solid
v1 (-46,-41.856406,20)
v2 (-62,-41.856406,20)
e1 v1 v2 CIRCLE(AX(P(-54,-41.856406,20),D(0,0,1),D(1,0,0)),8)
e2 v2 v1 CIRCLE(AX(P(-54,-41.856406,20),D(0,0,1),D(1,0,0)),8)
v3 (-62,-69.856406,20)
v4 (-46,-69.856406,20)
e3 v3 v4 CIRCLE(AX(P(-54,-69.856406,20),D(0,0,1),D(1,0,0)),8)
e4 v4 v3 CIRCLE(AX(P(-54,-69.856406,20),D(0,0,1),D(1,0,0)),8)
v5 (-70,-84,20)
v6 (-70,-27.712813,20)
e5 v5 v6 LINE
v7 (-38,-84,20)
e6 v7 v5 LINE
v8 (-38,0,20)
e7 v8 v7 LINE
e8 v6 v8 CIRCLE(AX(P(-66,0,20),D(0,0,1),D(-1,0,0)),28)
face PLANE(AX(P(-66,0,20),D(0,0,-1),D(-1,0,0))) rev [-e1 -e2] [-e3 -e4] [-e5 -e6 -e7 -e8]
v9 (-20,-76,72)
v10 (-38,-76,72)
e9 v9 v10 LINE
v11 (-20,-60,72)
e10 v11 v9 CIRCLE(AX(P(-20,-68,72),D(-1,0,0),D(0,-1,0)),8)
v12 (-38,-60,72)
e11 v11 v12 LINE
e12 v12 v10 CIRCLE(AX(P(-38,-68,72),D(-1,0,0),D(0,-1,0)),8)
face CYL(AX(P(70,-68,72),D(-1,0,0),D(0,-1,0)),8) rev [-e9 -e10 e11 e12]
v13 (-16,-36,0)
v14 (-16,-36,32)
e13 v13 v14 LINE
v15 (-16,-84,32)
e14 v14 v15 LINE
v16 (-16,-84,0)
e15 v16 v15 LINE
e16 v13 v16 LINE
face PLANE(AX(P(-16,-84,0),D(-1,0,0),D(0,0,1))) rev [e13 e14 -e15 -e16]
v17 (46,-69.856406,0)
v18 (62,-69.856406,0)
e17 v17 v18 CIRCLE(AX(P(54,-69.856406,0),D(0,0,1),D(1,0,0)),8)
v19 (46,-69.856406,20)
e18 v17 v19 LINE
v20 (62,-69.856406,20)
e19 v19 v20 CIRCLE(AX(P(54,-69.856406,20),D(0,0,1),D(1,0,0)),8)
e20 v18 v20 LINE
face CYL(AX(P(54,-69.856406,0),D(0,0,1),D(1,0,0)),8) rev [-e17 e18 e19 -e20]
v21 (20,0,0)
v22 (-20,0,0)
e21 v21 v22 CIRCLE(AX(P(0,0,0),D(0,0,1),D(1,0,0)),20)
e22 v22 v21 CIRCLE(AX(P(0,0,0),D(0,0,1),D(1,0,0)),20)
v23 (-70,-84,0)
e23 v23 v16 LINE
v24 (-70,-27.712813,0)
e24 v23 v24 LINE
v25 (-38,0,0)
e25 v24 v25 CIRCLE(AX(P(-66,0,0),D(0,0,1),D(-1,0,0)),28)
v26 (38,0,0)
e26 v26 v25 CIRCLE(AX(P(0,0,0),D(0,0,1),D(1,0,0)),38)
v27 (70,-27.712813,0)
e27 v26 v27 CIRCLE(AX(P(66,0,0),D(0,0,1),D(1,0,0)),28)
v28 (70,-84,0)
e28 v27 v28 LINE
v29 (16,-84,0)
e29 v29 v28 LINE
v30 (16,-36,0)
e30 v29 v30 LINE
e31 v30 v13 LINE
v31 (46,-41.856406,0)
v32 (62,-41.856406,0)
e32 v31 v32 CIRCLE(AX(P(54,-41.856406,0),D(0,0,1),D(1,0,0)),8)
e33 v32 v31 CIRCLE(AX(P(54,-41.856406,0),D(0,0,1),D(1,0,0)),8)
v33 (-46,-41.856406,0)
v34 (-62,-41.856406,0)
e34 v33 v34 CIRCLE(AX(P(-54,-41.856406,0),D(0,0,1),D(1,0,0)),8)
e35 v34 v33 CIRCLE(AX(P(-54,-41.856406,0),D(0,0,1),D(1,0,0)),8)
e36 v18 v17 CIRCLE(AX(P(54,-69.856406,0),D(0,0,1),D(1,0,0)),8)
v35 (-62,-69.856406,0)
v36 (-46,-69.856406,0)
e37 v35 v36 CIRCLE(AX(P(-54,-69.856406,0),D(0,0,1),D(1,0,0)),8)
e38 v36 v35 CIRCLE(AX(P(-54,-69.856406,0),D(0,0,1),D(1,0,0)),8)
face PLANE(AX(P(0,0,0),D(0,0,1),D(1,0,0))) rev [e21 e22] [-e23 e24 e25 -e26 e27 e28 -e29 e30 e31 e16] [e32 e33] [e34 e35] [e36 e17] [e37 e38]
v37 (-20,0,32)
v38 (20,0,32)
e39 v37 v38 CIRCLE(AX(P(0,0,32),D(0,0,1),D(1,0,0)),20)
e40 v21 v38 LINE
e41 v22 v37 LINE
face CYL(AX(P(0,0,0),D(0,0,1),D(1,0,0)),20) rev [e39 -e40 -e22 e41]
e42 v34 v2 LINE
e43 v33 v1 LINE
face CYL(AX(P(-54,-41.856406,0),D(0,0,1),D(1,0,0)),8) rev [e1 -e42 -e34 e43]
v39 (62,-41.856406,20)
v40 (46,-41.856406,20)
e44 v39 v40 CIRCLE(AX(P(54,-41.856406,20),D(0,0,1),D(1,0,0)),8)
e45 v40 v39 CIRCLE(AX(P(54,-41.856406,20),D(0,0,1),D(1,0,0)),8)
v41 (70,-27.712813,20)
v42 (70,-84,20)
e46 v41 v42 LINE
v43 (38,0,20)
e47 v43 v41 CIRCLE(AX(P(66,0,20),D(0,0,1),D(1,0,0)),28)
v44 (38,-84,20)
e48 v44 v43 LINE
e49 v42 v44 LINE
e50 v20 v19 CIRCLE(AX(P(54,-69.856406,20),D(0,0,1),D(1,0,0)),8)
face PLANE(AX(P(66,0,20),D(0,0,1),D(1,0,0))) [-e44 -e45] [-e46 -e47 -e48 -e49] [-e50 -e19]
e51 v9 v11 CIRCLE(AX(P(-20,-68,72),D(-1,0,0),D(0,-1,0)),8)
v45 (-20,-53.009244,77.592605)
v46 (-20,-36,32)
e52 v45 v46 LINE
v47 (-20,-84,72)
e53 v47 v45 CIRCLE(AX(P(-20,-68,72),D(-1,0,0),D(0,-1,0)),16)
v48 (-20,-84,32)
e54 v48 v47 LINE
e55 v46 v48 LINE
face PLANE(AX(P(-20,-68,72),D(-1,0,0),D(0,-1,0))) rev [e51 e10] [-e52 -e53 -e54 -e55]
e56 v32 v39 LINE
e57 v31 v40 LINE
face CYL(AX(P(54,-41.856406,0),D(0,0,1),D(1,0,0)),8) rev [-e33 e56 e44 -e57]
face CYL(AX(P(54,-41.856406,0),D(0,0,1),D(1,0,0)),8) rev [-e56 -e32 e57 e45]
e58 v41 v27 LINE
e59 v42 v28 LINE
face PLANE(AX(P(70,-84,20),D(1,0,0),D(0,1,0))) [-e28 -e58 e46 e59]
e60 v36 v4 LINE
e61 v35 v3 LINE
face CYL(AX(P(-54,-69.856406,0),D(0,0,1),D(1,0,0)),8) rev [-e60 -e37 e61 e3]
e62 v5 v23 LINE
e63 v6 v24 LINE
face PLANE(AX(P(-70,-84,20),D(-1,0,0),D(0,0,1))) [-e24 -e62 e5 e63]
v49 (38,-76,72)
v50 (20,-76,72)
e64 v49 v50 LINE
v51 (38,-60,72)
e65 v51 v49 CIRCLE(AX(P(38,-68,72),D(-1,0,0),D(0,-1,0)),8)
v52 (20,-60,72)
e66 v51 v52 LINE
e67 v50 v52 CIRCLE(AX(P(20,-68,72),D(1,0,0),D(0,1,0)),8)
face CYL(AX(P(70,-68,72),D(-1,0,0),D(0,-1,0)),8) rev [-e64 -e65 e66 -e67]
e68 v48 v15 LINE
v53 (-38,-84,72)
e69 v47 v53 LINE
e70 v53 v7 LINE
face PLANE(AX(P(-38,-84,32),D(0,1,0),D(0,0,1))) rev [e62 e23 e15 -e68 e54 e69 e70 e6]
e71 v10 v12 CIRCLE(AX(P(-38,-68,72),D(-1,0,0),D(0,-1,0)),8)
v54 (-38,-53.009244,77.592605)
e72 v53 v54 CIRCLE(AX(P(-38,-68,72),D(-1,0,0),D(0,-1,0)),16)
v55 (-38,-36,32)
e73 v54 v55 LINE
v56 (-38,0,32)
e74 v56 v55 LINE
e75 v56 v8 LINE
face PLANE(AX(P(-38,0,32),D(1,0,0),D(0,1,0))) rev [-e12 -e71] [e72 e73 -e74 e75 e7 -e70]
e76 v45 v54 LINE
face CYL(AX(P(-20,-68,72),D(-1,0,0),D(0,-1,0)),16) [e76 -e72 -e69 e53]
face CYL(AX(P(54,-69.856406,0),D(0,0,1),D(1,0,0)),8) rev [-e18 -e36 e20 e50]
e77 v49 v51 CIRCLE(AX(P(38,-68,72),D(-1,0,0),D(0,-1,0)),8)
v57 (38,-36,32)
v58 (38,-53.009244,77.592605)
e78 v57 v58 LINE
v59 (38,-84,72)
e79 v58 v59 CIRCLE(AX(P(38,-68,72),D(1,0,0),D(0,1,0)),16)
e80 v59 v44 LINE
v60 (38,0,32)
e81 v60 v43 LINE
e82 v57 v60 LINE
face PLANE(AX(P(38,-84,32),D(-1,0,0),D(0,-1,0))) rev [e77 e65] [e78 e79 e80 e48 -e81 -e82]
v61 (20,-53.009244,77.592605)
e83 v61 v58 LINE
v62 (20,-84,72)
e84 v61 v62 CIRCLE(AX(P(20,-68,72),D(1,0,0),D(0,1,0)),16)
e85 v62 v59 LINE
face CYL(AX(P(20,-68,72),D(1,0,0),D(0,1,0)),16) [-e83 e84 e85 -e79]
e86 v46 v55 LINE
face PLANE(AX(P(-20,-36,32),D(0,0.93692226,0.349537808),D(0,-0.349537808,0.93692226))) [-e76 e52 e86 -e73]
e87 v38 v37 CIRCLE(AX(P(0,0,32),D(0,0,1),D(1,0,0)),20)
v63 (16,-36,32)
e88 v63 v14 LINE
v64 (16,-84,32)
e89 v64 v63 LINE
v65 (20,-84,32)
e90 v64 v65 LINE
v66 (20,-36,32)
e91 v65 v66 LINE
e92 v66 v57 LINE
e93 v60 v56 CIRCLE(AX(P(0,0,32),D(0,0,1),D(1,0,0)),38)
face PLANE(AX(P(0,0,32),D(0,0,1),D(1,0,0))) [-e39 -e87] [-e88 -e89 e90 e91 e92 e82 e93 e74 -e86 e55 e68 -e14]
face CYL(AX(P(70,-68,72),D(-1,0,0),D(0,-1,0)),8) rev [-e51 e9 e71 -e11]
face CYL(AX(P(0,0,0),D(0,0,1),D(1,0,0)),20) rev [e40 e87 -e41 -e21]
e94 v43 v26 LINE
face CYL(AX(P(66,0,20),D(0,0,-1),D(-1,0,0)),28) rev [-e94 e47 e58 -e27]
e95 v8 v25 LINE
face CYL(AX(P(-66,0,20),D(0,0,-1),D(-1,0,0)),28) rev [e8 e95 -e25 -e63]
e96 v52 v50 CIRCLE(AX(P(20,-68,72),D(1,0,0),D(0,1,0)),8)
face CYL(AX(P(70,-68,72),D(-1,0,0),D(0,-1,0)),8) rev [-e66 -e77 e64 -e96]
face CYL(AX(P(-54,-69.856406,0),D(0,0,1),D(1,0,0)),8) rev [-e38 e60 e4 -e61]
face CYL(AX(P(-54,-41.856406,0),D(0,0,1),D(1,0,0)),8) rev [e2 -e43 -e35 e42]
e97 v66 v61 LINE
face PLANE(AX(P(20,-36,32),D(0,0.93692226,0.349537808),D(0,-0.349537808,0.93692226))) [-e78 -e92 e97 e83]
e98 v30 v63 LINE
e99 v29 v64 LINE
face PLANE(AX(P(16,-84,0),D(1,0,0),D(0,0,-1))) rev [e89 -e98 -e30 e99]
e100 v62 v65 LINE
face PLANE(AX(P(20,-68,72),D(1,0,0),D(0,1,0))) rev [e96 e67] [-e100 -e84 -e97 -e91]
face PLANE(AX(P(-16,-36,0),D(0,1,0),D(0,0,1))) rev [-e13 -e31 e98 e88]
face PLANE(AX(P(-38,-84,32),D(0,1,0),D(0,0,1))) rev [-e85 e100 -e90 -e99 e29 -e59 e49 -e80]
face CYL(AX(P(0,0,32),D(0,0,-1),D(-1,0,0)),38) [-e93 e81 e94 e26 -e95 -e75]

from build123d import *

# Parameters (mm, degrees)
BASE_BLOCK_DEPTH              = 32
FORK_ARMS_DEPTH               = 20
SIDE_FLANGE_DEPTH             = 18
FLANGE_START                  = -18
FLANGE_EXTENSION_DEPTH        = 18
FORK_SLOT_SKETCH_W            = 32
FORK_SLOT_SKETCH_H            = 48
FORK_SLOT_48X32_DEPTH         = 123.849501423
FORK_ARM_PROFILE_CUT_SKETCH_R = 8
FORK_ARM_PROFILE_CUT_DEPTH    = 129.763348823
FLANGE_HOLES_SKETCH_R         = 8
FLANGE_HOLES_16_DEPTH         = 163.677595261
PIVOT_BORE_SKETCH_R           = 20
PIVOT_BORE_40_DEPTH           = 123.849501423


with BuildPart() as part:
    # Base Block Sketch → Base Block (new body)
    with BuildSketch(Plane.XY):
        with BuildLine():
            Line((-38, 0), (-38, -84))
            Line((-38, -84), (38, -84))
            Line((38, -84), (38, 0))
            ThreePointArc((38, 0), (0, 38), (-38, 0))
        make_face()
    extrude(amount=BASE_BLOCK_DEPTH)

    # Fork Arms Sketch → Fork Arms (add)
    with BuildSketch(Plane(origin=(0, 0, 0), x_dir=(-1, 0, 0), z_dir=(0, 0, -1))):
        with BuildLine():
            Line((38, -84), (70, -84))
            Line((70, -84), (70, -27.712812921))
            ThreePointArc((70, -27.712812921), (47.66969722, -21.166010489), (38, 0))
            Line((38, 0), (38, -84))
        make_face()
        with BuildLine():
            Line((-38, -84), (-70, -84))
            Line((-70, -84), (-70, -27.712812921))
            ThreePointArc((-70, -27.712812921), (-47.66969722, -21.166010489), (-38, 0))
            Line((-38, 0), (-38, -84))
        make_face()
    extrude(amount=-FORK_ARMS_DEPTH)

    # Side Flange Sketch → Side Flange (add)
    with BuildSketch(Plane.ZY.offset(38)):
        with BuildLine():
            Line((72, -84), (32, -84))
            Line((32, -84), (32, -36))
            Line((32, -36), (77.592604925, -53.009243843))
            ThreePointArc((77.592604925, -53.009243843), (87.745667634, -70.841469822), (72, -84))
        make_face()
    extrude(amount=-SIDE_FLANGE_DEPTH)

    # Flange Extension Sketch → Flange Extension (add)
    with BuildSketch(Plane(origin=(38, 0, 0), x_dir=(0, 0, -1), z_dir=(1, 0, 0)).offset(FLANGE_START)):
        with BuildLine():
            Line((-72, -84), (-32, -84))
            Line((-32, -84), (-32, -36))
            Line((-32, -36), (-77.592604925, -53.009243843))
            ThreePointArc((-77.592604925, -53.009243843), (-87.745667634, -70.841469822), (-72, -84))
        make_face()
    extrude(amount=FLANGE_EXTENSION_DEPTH)

    # Fork Slot Sketch → Fork Slot 48x32 (cut, through all)
    with BuildSketch(Plane.XY.offset(32)):
        with Locations((0, -60)):
            Rectangle(FORK_SLOT_SKETCH_W, FORK_SLOT_SKETCH_H)
    extrude(amount=-FORK_SLOT_48X32_DEPTH, mode=Mode.SUBTRACT)

    # Fork Arm Profile Cut Sketch → Fork Arm Profile Cut (cut, through all)
    with BuildSketch(Plane.XY.offset(20)):
        with Locations((-54, -41.856406461)):
            Circle(FORK_ARM_PROFILE_CUT_SKETCH_R)
        with Locations((-54, -69.856406461)):
            Circle(FORK_ARM_PROFILE_CUT_SKETCH_R)
        with Locations((54, -41.856406461)):
            Circle(FORK_ARM_PROFILE_CUT_SKETCH_R)
        with Locations((54, -69.856406461)):
            Circle(FORK_ARM_PROFILE_CUT_SKETCH_R)
    extrude(amount=-FORK_ARM_PROFILE_CUT_DEPTH, mode=Mode.SUBTRACT)

    # Flange Holes Sketch → Flange Holes _16 (cut, through all)
    with BuildSketch(Plane.ZY.offset(38)):
        with Locations(Location((72, -68, 0), (0, 0, 270))):
            Circle(FLANGE_HOLES_SKETCH_R)
    extrude(amount=-FLANGE_HOLES_16_DEPTH, mode=Mode.SUBTRACT)

    # Pivot Bore Sketch → Pivot Bore _40 (cut, through all)
    with BuildSketch(Plane.XY.offset(32)):
        Circle(PIVOT_BORE_SKETCH_R)
    extrude(amount=-PIVOT_BORE_40_DEPTH, mode=Mode.SUBTRACT)


solid = part.part
